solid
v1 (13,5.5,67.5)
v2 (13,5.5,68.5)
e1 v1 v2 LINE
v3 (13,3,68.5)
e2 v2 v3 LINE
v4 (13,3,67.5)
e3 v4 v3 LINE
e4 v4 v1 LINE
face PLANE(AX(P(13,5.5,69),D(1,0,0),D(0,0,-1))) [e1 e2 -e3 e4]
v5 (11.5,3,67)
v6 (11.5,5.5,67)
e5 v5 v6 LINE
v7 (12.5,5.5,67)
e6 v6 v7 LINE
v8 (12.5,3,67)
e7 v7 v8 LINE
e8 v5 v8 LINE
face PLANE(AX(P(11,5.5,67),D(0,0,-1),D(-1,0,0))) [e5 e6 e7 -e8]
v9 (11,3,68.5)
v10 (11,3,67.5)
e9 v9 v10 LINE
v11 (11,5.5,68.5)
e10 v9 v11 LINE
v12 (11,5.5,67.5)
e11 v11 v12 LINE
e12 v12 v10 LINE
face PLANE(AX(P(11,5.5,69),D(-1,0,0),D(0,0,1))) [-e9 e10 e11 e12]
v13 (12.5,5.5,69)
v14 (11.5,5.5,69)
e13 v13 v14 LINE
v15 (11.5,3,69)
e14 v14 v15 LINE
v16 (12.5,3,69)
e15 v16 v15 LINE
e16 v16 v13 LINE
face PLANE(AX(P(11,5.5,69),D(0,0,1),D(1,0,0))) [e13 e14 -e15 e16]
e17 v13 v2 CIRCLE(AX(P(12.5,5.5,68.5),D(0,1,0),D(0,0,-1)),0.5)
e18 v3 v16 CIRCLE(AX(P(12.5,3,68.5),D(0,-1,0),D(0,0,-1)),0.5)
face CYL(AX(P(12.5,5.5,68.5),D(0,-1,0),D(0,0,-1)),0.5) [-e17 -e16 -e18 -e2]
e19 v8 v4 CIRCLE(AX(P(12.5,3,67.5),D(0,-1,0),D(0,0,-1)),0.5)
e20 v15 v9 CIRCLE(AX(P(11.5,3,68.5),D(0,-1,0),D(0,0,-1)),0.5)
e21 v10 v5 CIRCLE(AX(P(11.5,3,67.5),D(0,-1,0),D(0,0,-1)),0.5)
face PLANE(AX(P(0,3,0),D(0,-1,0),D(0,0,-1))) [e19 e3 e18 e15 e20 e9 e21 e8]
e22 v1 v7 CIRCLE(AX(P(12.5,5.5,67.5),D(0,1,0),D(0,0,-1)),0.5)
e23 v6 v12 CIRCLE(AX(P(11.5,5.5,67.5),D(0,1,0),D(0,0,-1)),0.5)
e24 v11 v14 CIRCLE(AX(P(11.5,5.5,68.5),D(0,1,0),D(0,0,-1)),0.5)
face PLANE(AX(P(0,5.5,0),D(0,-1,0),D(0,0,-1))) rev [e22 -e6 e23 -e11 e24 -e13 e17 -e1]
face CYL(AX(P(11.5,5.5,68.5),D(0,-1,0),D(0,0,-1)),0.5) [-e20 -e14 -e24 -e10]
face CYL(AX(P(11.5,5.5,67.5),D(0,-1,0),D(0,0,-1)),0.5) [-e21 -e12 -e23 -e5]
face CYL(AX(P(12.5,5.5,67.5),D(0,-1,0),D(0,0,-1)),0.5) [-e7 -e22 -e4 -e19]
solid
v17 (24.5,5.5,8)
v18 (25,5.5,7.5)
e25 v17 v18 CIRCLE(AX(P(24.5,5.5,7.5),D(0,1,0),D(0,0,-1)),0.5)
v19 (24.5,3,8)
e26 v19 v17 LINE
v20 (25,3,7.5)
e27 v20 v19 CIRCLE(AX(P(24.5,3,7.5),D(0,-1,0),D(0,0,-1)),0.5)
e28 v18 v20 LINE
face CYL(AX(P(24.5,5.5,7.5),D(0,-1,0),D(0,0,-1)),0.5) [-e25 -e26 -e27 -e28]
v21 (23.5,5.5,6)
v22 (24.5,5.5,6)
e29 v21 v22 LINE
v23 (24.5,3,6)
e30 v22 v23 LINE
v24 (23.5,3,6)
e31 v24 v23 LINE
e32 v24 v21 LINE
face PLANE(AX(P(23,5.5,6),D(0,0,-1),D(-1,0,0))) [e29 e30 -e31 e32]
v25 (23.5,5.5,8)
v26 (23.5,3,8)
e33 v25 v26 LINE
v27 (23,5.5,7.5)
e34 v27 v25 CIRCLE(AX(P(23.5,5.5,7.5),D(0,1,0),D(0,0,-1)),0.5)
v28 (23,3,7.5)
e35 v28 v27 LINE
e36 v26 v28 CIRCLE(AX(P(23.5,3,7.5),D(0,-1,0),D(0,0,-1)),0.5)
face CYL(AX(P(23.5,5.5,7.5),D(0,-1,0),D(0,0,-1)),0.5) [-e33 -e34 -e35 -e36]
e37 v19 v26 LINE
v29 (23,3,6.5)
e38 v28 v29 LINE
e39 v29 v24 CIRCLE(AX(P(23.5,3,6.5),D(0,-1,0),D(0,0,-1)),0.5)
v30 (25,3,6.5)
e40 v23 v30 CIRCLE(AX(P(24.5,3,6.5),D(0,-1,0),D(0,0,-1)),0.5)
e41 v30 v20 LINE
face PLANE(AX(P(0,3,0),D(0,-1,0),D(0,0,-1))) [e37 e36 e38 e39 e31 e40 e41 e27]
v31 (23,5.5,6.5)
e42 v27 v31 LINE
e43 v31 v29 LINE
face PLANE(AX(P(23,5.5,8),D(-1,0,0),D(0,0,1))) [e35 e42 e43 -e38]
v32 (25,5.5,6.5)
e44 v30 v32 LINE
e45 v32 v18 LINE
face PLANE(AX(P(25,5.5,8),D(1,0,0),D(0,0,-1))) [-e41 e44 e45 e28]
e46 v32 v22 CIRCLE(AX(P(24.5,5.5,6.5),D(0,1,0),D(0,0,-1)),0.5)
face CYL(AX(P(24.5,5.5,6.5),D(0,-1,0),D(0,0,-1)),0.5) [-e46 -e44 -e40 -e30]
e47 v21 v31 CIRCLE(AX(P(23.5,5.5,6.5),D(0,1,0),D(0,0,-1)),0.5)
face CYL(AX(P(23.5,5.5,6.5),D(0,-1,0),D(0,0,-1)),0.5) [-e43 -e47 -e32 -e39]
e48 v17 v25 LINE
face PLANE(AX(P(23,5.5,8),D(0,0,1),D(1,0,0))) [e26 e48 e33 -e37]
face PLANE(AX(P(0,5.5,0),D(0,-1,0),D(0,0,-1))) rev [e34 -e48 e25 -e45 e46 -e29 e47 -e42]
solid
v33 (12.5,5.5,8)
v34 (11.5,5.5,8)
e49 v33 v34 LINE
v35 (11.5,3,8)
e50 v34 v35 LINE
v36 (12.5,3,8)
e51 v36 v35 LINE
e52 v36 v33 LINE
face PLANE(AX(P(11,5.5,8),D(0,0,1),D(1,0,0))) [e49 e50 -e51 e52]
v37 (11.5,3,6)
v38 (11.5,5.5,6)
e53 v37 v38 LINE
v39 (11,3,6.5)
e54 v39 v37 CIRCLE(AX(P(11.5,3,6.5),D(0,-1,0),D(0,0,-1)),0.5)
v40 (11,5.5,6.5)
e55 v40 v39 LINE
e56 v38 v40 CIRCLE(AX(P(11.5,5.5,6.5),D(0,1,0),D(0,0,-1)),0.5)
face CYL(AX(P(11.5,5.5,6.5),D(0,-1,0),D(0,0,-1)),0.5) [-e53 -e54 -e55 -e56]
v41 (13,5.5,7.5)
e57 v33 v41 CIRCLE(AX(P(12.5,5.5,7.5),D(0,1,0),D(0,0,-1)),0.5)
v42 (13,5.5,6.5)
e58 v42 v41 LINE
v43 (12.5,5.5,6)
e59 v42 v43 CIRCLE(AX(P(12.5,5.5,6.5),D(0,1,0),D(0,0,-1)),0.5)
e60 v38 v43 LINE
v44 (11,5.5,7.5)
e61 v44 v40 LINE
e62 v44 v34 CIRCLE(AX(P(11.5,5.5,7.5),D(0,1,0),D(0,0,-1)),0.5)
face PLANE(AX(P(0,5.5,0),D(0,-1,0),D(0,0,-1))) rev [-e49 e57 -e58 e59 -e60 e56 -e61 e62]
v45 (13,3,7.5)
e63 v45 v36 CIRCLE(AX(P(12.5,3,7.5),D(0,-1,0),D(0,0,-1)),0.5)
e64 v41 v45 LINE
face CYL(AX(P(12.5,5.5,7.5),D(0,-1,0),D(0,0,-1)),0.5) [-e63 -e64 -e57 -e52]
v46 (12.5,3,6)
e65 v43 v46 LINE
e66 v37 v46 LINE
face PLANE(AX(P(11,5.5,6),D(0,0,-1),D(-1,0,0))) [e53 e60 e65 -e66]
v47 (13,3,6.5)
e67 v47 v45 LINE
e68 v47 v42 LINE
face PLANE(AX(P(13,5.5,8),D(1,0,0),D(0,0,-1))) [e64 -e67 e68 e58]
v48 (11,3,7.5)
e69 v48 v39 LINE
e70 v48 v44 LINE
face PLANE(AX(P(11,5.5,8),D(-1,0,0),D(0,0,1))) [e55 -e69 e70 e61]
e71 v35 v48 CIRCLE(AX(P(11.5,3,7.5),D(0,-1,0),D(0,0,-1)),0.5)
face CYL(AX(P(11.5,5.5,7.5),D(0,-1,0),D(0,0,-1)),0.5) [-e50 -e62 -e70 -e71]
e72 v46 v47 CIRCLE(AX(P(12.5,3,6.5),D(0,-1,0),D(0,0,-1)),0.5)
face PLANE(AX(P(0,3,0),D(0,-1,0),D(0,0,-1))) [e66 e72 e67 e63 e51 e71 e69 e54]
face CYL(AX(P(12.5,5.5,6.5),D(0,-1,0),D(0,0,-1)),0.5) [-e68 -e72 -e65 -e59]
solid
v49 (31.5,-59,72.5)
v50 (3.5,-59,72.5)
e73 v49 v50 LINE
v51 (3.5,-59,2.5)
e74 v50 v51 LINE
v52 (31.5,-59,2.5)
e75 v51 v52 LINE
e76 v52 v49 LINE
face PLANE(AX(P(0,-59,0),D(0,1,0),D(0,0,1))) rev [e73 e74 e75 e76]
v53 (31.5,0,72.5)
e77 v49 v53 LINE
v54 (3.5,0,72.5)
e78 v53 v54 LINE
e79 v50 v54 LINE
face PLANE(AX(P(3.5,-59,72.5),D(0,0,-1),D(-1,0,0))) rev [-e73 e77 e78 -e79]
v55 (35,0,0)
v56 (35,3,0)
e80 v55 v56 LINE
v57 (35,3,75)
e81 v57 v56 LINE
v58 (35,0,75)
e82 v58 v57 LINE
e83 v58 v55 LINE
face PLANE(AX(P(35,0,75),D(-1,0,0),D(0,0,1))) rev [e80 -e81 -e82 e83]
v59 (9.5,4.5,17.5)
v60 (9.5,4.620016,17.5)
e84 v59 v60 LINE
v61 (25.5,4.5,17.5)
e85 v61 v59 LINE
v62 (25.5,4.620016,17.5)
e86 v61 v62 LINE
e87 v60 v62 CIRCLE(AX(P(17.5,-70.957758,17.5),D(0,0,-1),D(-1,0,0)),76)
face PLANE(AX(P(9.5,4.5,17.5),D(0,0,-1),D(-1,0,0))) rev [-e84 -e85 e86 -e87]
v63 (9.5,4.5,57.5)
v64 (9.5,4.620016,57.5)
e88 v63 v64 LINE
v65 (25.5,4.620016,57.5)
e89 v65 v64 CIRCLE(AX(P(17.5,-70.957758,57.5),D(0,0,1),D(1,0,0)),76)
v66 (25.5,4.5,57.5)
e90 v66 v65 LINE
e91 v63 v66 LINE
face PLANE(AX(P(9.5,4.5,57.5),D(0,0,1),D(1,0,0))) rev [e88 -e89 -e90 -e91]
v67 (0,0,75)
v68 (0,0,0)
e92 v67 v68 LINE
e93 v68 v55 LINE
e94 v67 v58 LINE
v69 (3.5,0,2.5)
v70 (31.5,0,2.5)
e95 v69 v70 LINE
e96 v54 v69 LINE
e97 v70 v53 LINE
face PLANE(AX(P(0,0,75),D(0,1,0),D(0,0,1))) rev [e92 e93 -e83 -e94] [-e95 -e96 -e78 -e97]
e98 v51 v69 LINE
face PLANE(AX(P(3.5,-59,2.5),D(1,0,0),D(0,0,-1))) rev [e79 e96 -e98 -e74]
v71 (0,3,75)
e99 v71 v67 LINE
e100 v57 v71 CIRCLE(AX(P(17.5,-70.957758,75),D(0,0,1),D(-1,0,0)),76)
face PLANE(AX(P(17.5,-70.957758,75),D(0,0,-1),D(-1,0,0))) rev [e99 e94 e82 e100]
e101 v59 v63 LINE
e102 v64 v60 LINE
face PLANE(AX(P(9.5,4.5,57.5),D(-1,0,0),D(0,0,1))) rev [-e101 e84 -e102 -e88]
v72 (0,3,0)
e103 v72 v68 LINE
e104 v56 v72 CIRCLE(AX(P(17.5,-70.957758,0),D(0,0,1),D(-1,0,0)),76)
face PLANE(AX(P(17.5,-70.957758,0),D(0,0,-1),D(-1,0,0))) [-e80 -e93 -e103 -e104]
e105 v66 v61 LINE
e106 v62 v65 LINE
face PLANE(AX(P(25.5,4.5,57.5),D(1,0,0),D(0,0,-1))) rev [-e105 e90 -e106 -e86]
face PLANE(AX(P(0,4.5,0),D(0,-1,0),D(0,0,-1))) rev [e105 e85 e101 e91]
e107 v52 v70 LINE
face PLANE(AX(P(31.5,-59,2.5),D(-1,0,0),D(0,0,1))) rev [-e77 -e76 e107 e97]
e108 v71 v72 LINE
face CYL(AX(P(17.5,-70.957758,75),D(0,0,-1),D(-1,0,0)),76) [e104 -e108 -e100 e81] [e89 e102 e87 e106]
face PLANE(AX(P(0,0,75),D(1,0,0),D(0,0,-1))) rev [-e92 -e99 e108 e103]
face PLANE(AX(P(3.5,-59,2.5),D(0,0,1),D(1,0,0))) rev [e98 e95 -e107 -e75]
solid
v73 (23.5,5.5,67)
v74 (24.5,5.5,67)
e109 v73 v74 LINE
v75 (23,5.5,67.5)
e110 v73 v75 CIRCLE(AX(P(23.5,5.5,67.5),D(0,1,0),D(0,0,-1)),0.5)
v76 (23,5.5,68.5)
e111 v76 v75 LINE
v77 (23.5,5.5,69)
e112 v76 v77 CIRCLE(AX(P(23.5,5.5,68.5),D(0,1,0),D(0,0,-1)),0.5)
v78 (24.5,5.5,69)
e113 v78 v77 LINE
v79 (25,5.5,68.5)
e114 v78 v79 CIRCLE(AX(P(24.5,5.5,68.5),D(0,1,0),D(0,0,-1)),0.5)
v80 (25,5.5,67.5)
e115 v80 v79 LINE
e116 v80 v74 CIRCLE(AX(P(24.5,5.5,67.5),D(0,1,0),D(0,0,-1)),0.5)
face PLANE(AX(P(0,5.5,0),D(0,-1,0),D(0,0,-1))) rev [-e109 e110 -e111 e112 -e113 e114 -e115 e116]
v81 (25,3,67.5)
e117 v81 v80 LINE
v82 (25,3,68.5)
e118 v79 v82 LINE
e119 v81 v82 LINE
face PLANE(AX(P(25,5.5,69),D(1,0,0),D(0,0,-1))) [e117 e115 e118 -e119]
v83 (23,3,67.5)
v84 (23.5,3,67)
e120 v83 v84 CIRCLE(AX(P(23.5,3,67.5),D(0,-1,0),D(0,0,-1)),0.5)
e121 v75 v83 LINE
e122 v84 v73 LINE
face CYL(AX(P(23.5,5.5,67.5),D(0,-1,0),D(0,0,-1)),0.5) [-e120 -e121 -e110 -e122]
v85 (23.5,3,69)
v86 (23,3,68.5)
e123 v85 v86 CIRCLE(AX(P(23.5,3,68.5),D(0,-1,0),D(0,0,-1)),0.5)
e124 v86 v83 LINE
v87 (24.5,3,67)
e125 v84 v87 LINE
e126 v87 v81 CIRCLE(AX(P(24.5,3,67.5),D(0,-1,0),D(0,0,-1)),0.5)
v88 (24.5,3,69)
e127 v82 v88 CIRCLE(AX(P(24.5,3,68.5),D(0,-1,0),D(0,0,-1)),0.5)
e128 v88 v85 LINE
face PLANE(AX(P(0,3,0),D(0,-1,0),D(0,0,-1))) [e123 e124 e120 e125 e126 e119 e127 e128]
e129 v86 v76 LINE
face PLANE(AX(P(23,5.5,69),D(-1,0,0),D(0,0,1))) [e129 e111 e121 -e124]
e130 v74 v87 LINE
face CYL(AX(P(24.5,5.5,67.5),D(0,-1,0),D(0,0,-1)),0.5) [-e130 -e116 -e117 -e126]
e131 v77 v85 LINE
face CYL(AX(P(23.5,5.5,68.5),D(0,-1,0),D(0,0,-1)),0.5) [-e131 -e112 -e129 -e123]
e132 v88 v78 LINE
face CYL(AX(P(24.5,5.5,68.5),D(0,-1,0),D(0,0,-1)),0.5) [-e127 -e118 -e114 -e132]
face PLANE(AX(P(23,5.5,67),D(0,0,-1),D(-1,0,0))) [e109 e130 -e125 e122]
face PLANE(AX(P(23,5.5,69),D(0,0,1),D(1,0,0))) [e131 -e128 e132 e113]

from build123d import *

# Parameters (mm, degrees)
BOSS_EXTRUDE1_DEPTH   = 75
SKETCH2_W             = 16
SKETCH2_H             = 40
CUT_EXTRUDE1_DEPTH    = 1
SKETCH4_W             = 2
SKETCH4_H             = 2
BOSS_EXTRUDE2_DEPTH   = 2.5
BOSS_EXTRUDE2_2_DEPTH = 2.5
BOSS_EXTRUDE2_3_DEPTH = 2.5
BOSS_EXTRUDE2_4_DEPTH = 2.5
FILLET1_R             = 0.5
FILLET2_R             = 0.5
FILLET3_R             = 0.5
FILLET4_R             = 0.5
SKETCH5_W             = 28
SKETCH5_H             = 70
BOSS_EXTRUDE3_DEPTH   = 59


with BuildPart() as part:
    # Sketch1 → Boss-Extrude1 (new body)
    with BuildSketch(Plane.XY):
        with BuildLine():
            Line((0, 0), (35, 0))
            Line((35, 0), (35, 3))
            ThreePointArc((35, 3), (17.5, 5.042241786), (0, 3))
            Line((0, 3), (0, 0))
        make_face()
    extrude(amount=BOSS_EXTRUDE1_DEPTH)

    # Sketch2 → Cut-Extrude1 (cut)
    with BuildSketch(Plane(origin=(0, 5.5, 0), x_dir=(1, 0, 0), z_dir=(0, 1, 0))):
        with Locations((17.5, -37.5)):
            Rectangle(SKETCH2_W, SKETCH2_H)
    extrude(amount=-CUT_EXTRUDE1_DEPTH, mode=Mode.SUBTRACT)

    # Sketch5 → Boss-Extrude3 (add)
    with BuildSketch(Plane.XZ):
        with Locations((17.5, 37.5)):
            Rectangle(SKETCH5_W, SKETCH5_H)
    extrude(amount=BOSS_EXTRUDE3_DEPTH)


with BuildPart() as body_2:
    # Sketch4 → Boss-Extrude2 (new body)
    with BuildSketch(Plane(origin=(0, 3, 0), x_dir=(-1, 0, 0), z_dir=(0, -1, 0))):
        with Locations((-12, -68)):
            Rectangle(SKETCH4_W, SKETCH4_H)
    extrude(amount=-BOSS_EXTRUDE2_DEPTH)

    # Fillet1
    fillet1_edges = [body_2.edges().sort_by_distance(p)[0] for p in [
        (11, 4.25, 69),
        (13, 4.25, 69),
        (13, 4.25, 67),
        (11, 4.25, 67),
    ]]
    fillet(fillet1_edges, radius=FILLET1_R)


with BuildPart() as body_3:
    # Sketch4 → Boss-Extrude2 2 (new body)
    with BuildSketch(Plane(origin=(0, 3, 0), x_dir=(-1, 0, 0), z_dir=(0, -1, 0))):
        with Locations((-24, -68)):
            Rectangle(SKETCH4_W, SKETCH4_H)
    extrude(amount=-BOSS_EXTRUDE2_2_DEPTH)

    # Fillet2
    fillet2_edges = [body_3.edges().sort_by_distance(p)[0] for p in [
        (23, 4.25, 69),
        (25, 4.25, 69),
        (25, 4.25, 67),
        (23, 4.25, 67),
    ]]
    fillet(fillet2_edges, radius=FILLET2_R)


with BuildPart() as body_4:
    # Sketch4 → Boss-Extrude2 3 (new body)
    with BuildSketch(Plane(origin=(0, 3, 0), x_dir=(-1, 0, 0), z_dir=(0, -1, 0))):
        with Locations((-12, -7)):
            Rectangle(SKETCH4_W, SKETCH4_H)
    extrude(amount=-BOSS_EXTRUDE2_3_DEPTH)

    # Fillet3
    fillet3_edges = [body_4.edges().sort_by_distance(p)[0] for p in [
        (11, 4.25, 8),
        (13, 4.25, 8),
        (13, 4.25, 6),
        (11, 4.25, 6),
    ]]
    fillet(fillet3_edges, radius=FILLET3_R)


with BuildPart() as body_5:
    # Sketch4 → Boss-Extrude2 4 (new body)
    with BuildSketch(Plane(origin=(0, 3, 0), x_dir=(-1, 0, 0), z_dir=(0, -1, 0))):
        with Locations((-24, -7)):
            Rectangle(SKETCH4_W, SKETCH4_H)
    extrude(amount=-BOSS_EXTRUDE2_4_DEPTH)

    # Fillet4
    fillet4_edges = [body_5.edges().sort_by_distance(p)[0] for p in [
        (23, 4.25, 8),
        (25, 4.25, 8),
        (25, 4.25, 6),
        (23, 4.25, 6),
    ]]
    fillet(fillet4_edges, radius=FILLET4_R)


solid = Compound([part.part, body_2.part, body_3.part, body_4.part, body_5.part])
